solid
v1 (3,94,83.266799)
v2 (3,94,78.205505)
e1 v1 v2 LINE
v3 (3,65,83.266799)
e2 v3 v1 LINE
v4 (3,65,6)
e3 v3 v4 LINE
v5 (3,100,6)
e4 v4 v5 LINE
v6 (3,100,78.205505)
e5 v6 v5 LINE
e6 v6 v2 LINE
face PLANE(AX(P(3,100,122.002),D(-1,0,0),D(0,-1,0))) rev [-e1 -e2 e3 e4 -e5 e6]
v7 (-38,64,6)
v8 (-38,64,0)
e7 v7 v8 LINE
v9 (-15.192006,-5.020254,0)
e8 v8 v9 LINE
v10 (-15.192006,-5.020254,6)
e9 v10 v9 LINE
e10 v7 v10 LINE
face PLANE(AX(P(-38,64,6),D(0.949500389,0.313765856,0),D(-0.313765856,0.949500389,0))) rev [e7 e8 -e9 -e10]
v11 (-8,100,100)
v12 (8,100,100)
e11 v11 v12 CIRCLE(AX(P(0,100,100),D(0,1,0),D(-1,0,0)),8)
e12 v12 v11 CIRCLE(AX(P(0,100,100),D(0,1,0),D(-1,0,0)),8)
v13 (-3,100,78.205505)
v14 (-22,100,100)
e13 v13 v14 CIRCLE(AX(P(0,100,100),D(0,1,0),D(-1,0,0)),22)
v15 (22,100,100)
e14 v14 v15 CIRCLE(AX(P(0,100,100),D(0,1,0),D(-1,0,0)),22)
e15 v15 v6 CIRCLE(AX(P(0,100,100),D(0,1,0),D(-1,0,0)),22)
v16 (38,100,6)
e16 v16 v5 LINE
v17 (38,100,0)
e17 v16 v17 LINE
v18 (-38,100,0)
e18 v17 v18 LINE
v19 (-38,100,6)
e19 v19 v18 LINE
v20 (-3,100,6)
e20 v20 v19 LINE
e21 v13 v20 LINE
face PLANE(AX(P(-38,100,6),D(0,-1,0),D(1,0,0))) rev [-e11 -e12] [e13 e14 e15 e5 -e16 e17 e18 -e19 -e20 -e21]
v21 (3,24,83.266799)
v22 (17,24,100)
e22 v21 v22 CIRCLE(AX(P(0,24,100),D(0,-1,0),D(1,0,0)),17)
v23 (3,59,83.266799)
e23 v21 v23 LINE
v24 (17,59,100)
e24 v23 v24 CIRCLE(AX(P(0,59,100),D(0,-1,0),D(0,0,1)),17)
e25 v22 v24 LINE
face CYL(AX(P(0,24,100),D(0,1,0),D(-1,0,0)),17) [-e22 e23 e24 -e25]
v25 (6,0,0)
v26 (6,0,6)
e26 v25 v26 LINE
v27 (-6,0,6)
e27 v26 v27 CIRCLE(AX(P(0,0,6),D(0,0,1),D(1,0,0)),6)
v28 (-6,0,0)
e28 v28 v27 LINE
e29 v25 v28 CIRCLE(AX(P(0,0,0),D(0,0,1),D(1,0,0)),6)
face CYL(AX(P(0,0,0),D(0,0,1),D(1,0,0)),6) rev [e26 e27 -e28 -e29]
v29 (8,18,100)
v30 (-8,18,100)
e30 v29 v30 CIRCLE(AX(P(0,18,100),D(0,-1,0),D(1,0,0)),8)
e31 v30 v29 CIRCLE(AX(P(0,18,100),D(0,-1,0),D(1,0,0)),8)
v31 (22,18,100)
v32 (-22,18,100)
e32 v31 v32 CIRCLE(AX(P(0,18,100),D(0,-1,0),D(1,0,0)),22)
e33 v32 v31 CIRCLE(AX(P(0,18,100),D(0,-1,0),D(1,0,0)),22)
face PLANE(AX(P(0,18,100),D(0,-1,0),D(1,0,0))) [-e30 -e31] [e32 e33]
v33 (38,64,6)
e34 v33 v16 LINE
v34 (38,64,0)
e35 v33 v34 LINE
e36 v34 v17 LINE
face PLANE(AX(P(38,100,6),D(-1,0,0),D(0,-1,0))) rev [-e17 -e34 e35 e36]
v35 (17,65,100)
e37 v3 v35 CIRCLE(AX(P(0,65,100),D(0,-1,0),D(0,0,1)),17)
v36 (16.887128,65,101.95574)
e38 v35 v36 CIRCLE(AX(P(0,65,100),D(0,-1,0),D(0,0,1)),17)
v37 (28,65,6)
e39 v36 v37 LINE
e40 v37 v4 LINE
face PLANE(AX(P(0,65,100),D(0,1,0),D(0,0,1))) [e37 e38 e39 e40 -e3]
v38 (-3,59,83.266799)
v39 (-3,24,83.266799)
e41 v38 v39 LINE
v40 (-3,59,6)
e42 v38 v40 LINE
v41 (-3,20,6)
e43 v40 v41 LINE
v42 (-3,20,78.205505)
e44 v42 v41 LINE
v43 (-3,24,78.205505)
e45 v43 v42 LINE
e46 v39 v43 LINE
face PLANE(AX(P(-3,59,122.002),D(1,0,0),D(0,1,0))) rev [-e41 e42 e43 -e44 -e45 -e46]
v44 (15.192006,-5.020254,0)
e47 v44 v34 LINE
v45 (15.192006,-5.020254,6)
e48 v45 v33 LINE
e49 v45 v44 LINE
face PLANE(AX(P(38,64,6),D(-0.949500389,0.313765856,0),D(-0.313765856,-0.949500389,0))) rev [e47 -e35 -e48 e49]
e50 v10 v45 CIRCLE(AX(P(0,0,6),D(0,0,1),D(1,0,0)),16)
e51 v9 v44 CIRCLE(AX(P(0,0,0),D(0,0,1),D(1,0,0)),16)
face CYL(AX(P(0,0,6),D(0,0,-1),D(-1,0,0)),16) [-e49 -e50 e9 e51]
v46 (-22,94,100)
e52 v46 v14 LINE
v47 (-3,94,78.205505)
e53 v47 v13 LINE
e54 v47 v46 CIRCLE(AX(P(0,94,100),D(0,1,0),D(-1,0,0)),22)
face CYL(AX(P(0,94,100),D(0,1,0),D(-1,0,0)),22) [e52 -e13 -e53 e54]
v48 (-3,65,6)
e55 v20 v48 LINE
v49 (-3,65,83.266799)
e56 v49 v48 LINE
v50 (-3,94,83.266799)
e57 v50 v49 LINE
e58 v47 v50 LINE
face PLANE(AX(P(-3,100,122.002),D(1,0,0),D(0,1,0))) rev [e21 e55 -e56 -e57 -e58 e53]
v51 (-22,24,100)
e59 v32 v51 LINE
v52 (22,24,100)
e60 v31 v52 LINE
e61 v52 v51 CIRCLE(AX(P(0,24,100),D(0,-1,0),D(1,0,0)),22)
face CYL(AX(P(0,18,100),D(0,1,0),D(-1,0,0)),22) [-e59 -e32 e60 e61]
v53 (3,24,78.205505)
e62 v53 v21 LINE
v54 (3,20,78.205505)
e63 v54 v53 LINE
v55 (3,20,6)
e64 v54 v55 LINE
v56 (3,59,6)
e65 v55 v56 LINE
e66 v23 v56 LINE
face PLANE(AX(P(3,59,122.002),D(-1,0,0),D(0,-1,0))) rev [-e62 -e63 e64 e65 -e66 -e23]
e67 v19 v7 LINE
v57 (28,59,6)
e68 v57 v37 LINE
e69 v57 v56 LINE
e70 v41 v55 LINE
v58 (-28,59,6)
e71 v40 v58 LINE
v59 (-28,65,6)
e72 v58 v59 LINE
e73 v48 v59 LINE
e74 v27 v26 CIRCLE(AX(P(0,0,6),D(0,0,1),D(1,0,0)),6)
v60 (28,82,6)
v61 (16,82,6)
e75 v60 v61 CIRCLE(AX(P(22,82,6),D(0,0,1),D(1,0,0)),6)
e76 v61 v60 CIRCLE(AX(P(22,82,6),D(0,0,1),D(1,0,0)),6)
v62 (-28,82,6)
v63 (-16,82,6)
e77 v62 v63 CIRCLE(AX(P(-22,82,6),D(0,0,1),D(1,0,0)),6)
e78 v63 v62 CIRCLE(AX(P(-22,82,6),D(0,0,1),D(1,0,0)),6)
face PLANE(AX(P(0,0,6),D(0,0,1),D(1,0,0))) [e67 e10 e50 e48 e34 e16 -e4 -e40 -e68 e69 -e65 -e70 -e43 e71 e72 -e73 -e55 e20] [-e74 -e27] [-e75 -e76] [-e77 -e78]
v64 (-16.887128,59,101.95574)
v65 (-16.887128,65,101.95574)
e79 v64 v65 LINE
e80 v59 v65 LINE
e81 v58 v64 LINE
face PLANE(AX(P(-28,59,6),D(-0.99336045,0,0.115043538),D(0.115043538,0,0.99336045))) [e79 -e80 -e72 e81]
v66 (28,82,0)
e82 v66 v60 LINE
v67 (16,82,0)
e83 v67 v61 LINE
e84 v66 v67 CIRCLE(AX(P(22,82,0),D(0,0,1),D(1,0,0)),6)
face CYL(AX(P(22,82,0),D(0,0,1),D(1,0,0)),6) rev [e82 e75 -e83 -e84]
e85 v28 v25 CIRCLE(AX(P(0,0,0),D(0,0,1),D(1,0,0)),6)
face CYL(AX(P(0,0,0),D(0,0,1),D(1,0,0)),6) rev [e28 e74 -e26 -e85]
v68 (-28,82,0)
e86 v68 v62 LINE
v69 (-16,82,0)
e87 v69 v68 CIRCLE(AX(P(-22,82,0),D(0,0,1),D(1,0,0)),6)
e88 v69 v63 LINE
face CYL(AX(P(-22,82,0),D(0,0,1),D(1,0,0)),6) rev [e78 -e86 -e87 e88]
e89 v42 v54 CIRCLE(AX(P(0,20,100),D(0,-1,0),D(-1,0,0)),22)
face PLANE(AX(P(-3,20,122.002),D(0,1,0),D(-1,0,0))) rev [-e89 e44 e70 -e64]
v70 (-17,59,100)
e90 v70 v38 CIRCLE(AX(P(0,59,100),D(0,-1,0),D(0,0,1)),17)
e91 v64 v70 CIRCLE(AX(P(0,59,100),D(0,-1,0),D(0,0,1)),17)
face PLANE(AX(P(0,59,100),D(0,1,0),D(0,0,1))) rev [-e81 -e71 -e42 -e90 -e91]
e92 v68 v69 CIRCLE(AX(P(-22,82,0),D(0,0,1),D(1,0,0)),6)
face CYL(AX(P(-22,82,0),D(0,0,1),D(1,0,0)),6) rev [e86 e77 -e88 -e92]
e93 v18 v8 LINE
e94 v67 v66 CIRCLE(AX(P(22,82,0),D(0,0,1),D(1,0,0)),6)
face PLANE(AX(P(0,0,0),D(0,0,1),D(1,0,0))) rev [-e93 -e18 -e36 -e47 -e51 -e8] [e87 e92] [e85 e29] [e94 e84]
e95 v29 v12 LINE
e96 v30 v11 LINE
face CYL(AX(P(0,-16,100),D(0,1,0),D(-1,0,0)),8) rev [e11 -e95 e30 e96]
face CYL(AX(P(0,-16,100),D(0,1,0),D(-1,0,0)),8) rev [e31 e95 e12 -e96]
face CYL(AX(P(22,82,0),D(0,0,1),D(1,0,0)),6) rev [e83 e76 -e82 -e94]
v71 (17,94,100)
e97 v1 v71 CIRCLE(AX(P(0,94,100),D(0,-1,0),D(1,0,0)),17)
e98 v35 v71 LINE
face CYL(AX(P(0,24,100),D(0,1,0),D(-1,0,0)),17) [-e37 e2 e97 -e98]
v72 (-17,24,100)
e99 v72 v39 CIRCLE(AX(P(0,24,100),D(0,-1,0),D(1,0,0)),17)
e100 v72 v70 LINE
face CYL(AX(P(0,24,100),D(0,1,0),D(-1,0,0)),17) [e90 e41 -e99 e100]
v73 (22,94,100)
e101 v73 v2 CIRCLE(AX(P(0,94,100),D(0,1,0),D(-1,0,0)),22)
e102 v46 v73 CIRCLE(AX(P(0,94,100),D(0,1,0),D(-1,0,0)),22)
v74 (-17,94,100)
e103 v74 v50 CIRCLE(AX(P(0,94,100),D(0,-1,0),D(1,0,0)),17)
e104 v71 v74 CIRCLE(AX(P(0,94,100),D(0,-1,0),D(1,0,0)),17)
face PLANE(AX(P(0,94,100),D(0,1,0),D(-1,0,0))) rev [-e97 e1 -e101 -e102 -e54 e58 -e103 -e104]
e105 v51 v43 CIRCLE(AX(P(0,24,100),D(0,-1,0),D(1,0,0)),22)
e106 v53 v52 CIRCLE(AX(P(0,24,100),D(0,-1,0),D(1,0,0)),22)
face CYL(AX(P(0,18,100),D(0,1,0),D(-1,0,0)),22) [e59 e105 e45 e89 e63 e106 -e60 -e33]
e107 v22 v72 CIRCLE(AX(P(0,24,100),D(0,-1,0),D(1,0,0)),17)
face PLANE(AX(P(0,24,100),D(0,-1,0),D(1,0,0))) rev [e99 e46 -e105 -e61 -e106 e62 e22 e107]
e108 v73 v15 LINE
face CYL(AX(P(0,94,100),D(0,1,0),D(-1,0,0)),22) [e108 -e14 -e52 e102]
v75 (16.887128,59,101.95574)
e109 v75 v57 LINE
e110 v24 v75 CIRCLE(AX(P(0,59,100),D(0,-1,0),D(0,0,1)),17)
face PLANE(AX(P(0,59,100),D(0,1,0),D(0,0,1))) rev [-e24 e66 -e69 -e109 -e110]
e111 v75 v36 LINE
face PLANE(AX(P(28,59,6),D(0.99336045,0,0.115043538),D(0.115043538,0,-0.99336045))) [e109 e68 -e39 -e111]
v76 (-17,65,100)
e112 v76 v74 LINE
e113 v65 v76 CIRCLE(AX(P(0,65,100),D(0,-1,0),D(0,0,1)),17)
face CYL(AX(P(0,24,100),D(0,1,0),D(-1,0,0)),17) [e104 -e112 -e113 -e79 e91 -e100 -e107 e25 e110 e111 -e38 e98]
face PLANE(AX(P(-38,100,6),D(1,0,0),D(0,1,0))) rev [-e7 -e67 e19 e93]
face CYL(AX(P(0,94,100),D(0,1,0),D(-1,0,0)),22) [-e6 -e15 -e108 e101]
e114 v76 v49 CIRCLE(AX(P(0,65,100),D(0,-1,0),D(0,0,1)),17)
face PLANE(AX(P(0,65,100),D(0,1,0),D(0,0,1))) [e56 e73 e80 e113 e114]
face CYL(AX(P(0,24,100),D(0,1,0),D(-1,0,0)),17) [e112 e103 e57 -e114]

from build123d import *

# Parameters (mm, degrees)
WALL_PLATE_DEPTH           = 6
LOWER_FLANGE_SKETCH_R      = 22
LOWER_FLANGE_44_DEPTH      = 6
PIVOT_BOSS_SKETCH_R        = 17
PIVOT_BOSS_34_DEPTH        = 70
UPPER_FLANGE_SKETCH_R      = 22
UPPER_FLANGE_DEPTH         = 6
PIVOT_BORE_SKETCH_R        = 8
PIVOT_BORE_16_DEPTH        = 173.580416038
SUPPORT_ARM_DEPTH          = 6
ARM_WEB_REACH              = 159.797
ARM_WEB_SKETCH_W           = 6
ARM_WEB_SKETCH_H           = 35
MOUNTING_HOLES_SKETCH_R    = 6
MOUNTING_HOLES_3X_12_DEPTH = 6
GUSSET_RIB_REACH           = 159.797
GUSSET_RIB_SKETCH_W        = 6
GUSSET_RIB_SKETCH_H        = 39


with BuildPart() as part:
    # Wall Plate Sketch → Wall Plate (new body)
    with BuildSketch(Plane.XY):
        with BuildLine():
            Line((-38, 64), (-15.192006216, -5.020253691))
            ThreePointArc((-15.192006216, -5.020253691), (0, -16), (15.192006216, -5.020253691))
            Line((15.192006216, -5.020253691), (38, 64))
            Line((38, 64), (38, 100))
            Line((38, 100), (-38, 100))
            Line((-38, 100), (-38, 64))
        make_face()
    extrude(amount=WALL_PLATE_DEPTH)



with BuildPart() as body_2:
    # Lower Flange Sketch → Lower Flange Ø44 (new body)
    with BuildSketch(Plane(origin=(0, 100, 0), x_dir=(1, 0, 0), z_dir=(0, 1, 0))):
        with Locations(Location((0, -100, 0), (0, 0, 180))):
            Circle(LOWER_FLANGE_SKETCH_R)
    extrude(amount=-LOWER_FLANGE_44_DEPTH)

    # Pivot Boss Sketch → Pivot Boss Ø34 (add)
    with BuildSketch(Plane.XZ.offset(-94)):
        with Locations((0, 100)):
            Circle(PIVOT_BOSS_SKETCH_R)
    extrude(amount=PIVOT_BOSS_34_DEPTH)

    # Upper Flange Sketch → Upper Flange (add)
    with BuildSketch(Plane.XZ.offset(-24)):
        with Locations(Location((0, 100, 0), (0, 0, 180))):
            Circle(UPPER_FLANGE_SKETCH_R)
    extrude(amount=UPPER_FLANGE_DEPTH)

    # Pivot Bore Sketch → Pivot Bore Ø16 (cut, through all)
    with BuildSketch(Plane(origin=(0, 100, 0), x_dir=(1, 0, 0), z_dir=(0, 1, 0))):
        with Locations(Location((0, -100, 0), (0, 0, 180))):
            Circle(PIVOT_BORE_SKETCH_R)
    extrude(amount=-PIVOT_BORE_16_DEPTH, mode=Mode.SUBTRACT)


with BuildPart() as part_1:
    add(part.part)

    add(body_2.part)  # Support Arm merges body 2
    # Support Arm Sketch → Support Arm (add)
    with BuildSketch(Plane(origin=(0, 65, 0), x_dir=(1, 0, 0), z_dir=(0, 1, 0))):
        with BuildLine():
            Line((-28, -6), (28, -6))
            Line((28, -6), (16.887127656, -101.955740153))
            ThreePointArc((16.887127656, -101.955740153), (0, -83), (-16.887127656, -101.955740153))
            Line((-16.887127656, -101.955740153), (-28, -6))
        make_face()
    extrude(amount=-SUPPORT_ARM_DEPTH)

    # Arm Web Sketch → Arm Web (add, up to next)
    with BuildSketch(Plane.XY.offset(6), mode=Mode.PRIVATE) as arm_web_sk1:
        with Locations((0, 82.5)):
            Rectangle(ARM_WEB_SKETCH_W, ARM_WEB_SKETCH_H)
    arm_web_tool1 = extrude(arm_web_sk1.sketch, amount=ARM_WEB_REACH, mode=Mode.PRIVATE) - part_1.part
    add(arm_web_tool1.solids().sort_by_distance((0, 82.5, 6))[0])

    # Mounting Holes Sketch → Mounting Holes 3xØ12 (cut)
    with BuildSketch(Plane.XY.offset(6)):
        Circle(MOUNTING_HOLES_SKETCH_R)
        with Locations((-22, 82)):
            Circle(MOUNTING_HOLES_SKETCH_R)
        with Locations((22, 82)):
            Circle(MOUNTING_HOLES_SKETCH_R)
    extrude(amount=-MOUNTING_HOLES_3X_12_DEPTH, mode=Mode.SUBTRACT)

    # Gusset Rib Sketch → Gusset Rib (add, up to next)
    with BuildSketch(Plane.XY.offset(6), mode=Mode.PRIVATE) as gusset_rib_sk1:
        with Locations((0, 39.5)):
            Rectangle(GUSSET_RIB_SKETCH_W, GUSSET_RIB_SKETCH_H)
    gusset_rib_tool1 = extrude(gusset_rib_sk1.sketch, amount=GUSSET_RIB_REACH, mode=Mode.PRIVATE) - part_1.part
    add(gusset_rib_tool1.solids().sort_by_distance((0, 39.5, 6))[0])


solid = part_1.part
